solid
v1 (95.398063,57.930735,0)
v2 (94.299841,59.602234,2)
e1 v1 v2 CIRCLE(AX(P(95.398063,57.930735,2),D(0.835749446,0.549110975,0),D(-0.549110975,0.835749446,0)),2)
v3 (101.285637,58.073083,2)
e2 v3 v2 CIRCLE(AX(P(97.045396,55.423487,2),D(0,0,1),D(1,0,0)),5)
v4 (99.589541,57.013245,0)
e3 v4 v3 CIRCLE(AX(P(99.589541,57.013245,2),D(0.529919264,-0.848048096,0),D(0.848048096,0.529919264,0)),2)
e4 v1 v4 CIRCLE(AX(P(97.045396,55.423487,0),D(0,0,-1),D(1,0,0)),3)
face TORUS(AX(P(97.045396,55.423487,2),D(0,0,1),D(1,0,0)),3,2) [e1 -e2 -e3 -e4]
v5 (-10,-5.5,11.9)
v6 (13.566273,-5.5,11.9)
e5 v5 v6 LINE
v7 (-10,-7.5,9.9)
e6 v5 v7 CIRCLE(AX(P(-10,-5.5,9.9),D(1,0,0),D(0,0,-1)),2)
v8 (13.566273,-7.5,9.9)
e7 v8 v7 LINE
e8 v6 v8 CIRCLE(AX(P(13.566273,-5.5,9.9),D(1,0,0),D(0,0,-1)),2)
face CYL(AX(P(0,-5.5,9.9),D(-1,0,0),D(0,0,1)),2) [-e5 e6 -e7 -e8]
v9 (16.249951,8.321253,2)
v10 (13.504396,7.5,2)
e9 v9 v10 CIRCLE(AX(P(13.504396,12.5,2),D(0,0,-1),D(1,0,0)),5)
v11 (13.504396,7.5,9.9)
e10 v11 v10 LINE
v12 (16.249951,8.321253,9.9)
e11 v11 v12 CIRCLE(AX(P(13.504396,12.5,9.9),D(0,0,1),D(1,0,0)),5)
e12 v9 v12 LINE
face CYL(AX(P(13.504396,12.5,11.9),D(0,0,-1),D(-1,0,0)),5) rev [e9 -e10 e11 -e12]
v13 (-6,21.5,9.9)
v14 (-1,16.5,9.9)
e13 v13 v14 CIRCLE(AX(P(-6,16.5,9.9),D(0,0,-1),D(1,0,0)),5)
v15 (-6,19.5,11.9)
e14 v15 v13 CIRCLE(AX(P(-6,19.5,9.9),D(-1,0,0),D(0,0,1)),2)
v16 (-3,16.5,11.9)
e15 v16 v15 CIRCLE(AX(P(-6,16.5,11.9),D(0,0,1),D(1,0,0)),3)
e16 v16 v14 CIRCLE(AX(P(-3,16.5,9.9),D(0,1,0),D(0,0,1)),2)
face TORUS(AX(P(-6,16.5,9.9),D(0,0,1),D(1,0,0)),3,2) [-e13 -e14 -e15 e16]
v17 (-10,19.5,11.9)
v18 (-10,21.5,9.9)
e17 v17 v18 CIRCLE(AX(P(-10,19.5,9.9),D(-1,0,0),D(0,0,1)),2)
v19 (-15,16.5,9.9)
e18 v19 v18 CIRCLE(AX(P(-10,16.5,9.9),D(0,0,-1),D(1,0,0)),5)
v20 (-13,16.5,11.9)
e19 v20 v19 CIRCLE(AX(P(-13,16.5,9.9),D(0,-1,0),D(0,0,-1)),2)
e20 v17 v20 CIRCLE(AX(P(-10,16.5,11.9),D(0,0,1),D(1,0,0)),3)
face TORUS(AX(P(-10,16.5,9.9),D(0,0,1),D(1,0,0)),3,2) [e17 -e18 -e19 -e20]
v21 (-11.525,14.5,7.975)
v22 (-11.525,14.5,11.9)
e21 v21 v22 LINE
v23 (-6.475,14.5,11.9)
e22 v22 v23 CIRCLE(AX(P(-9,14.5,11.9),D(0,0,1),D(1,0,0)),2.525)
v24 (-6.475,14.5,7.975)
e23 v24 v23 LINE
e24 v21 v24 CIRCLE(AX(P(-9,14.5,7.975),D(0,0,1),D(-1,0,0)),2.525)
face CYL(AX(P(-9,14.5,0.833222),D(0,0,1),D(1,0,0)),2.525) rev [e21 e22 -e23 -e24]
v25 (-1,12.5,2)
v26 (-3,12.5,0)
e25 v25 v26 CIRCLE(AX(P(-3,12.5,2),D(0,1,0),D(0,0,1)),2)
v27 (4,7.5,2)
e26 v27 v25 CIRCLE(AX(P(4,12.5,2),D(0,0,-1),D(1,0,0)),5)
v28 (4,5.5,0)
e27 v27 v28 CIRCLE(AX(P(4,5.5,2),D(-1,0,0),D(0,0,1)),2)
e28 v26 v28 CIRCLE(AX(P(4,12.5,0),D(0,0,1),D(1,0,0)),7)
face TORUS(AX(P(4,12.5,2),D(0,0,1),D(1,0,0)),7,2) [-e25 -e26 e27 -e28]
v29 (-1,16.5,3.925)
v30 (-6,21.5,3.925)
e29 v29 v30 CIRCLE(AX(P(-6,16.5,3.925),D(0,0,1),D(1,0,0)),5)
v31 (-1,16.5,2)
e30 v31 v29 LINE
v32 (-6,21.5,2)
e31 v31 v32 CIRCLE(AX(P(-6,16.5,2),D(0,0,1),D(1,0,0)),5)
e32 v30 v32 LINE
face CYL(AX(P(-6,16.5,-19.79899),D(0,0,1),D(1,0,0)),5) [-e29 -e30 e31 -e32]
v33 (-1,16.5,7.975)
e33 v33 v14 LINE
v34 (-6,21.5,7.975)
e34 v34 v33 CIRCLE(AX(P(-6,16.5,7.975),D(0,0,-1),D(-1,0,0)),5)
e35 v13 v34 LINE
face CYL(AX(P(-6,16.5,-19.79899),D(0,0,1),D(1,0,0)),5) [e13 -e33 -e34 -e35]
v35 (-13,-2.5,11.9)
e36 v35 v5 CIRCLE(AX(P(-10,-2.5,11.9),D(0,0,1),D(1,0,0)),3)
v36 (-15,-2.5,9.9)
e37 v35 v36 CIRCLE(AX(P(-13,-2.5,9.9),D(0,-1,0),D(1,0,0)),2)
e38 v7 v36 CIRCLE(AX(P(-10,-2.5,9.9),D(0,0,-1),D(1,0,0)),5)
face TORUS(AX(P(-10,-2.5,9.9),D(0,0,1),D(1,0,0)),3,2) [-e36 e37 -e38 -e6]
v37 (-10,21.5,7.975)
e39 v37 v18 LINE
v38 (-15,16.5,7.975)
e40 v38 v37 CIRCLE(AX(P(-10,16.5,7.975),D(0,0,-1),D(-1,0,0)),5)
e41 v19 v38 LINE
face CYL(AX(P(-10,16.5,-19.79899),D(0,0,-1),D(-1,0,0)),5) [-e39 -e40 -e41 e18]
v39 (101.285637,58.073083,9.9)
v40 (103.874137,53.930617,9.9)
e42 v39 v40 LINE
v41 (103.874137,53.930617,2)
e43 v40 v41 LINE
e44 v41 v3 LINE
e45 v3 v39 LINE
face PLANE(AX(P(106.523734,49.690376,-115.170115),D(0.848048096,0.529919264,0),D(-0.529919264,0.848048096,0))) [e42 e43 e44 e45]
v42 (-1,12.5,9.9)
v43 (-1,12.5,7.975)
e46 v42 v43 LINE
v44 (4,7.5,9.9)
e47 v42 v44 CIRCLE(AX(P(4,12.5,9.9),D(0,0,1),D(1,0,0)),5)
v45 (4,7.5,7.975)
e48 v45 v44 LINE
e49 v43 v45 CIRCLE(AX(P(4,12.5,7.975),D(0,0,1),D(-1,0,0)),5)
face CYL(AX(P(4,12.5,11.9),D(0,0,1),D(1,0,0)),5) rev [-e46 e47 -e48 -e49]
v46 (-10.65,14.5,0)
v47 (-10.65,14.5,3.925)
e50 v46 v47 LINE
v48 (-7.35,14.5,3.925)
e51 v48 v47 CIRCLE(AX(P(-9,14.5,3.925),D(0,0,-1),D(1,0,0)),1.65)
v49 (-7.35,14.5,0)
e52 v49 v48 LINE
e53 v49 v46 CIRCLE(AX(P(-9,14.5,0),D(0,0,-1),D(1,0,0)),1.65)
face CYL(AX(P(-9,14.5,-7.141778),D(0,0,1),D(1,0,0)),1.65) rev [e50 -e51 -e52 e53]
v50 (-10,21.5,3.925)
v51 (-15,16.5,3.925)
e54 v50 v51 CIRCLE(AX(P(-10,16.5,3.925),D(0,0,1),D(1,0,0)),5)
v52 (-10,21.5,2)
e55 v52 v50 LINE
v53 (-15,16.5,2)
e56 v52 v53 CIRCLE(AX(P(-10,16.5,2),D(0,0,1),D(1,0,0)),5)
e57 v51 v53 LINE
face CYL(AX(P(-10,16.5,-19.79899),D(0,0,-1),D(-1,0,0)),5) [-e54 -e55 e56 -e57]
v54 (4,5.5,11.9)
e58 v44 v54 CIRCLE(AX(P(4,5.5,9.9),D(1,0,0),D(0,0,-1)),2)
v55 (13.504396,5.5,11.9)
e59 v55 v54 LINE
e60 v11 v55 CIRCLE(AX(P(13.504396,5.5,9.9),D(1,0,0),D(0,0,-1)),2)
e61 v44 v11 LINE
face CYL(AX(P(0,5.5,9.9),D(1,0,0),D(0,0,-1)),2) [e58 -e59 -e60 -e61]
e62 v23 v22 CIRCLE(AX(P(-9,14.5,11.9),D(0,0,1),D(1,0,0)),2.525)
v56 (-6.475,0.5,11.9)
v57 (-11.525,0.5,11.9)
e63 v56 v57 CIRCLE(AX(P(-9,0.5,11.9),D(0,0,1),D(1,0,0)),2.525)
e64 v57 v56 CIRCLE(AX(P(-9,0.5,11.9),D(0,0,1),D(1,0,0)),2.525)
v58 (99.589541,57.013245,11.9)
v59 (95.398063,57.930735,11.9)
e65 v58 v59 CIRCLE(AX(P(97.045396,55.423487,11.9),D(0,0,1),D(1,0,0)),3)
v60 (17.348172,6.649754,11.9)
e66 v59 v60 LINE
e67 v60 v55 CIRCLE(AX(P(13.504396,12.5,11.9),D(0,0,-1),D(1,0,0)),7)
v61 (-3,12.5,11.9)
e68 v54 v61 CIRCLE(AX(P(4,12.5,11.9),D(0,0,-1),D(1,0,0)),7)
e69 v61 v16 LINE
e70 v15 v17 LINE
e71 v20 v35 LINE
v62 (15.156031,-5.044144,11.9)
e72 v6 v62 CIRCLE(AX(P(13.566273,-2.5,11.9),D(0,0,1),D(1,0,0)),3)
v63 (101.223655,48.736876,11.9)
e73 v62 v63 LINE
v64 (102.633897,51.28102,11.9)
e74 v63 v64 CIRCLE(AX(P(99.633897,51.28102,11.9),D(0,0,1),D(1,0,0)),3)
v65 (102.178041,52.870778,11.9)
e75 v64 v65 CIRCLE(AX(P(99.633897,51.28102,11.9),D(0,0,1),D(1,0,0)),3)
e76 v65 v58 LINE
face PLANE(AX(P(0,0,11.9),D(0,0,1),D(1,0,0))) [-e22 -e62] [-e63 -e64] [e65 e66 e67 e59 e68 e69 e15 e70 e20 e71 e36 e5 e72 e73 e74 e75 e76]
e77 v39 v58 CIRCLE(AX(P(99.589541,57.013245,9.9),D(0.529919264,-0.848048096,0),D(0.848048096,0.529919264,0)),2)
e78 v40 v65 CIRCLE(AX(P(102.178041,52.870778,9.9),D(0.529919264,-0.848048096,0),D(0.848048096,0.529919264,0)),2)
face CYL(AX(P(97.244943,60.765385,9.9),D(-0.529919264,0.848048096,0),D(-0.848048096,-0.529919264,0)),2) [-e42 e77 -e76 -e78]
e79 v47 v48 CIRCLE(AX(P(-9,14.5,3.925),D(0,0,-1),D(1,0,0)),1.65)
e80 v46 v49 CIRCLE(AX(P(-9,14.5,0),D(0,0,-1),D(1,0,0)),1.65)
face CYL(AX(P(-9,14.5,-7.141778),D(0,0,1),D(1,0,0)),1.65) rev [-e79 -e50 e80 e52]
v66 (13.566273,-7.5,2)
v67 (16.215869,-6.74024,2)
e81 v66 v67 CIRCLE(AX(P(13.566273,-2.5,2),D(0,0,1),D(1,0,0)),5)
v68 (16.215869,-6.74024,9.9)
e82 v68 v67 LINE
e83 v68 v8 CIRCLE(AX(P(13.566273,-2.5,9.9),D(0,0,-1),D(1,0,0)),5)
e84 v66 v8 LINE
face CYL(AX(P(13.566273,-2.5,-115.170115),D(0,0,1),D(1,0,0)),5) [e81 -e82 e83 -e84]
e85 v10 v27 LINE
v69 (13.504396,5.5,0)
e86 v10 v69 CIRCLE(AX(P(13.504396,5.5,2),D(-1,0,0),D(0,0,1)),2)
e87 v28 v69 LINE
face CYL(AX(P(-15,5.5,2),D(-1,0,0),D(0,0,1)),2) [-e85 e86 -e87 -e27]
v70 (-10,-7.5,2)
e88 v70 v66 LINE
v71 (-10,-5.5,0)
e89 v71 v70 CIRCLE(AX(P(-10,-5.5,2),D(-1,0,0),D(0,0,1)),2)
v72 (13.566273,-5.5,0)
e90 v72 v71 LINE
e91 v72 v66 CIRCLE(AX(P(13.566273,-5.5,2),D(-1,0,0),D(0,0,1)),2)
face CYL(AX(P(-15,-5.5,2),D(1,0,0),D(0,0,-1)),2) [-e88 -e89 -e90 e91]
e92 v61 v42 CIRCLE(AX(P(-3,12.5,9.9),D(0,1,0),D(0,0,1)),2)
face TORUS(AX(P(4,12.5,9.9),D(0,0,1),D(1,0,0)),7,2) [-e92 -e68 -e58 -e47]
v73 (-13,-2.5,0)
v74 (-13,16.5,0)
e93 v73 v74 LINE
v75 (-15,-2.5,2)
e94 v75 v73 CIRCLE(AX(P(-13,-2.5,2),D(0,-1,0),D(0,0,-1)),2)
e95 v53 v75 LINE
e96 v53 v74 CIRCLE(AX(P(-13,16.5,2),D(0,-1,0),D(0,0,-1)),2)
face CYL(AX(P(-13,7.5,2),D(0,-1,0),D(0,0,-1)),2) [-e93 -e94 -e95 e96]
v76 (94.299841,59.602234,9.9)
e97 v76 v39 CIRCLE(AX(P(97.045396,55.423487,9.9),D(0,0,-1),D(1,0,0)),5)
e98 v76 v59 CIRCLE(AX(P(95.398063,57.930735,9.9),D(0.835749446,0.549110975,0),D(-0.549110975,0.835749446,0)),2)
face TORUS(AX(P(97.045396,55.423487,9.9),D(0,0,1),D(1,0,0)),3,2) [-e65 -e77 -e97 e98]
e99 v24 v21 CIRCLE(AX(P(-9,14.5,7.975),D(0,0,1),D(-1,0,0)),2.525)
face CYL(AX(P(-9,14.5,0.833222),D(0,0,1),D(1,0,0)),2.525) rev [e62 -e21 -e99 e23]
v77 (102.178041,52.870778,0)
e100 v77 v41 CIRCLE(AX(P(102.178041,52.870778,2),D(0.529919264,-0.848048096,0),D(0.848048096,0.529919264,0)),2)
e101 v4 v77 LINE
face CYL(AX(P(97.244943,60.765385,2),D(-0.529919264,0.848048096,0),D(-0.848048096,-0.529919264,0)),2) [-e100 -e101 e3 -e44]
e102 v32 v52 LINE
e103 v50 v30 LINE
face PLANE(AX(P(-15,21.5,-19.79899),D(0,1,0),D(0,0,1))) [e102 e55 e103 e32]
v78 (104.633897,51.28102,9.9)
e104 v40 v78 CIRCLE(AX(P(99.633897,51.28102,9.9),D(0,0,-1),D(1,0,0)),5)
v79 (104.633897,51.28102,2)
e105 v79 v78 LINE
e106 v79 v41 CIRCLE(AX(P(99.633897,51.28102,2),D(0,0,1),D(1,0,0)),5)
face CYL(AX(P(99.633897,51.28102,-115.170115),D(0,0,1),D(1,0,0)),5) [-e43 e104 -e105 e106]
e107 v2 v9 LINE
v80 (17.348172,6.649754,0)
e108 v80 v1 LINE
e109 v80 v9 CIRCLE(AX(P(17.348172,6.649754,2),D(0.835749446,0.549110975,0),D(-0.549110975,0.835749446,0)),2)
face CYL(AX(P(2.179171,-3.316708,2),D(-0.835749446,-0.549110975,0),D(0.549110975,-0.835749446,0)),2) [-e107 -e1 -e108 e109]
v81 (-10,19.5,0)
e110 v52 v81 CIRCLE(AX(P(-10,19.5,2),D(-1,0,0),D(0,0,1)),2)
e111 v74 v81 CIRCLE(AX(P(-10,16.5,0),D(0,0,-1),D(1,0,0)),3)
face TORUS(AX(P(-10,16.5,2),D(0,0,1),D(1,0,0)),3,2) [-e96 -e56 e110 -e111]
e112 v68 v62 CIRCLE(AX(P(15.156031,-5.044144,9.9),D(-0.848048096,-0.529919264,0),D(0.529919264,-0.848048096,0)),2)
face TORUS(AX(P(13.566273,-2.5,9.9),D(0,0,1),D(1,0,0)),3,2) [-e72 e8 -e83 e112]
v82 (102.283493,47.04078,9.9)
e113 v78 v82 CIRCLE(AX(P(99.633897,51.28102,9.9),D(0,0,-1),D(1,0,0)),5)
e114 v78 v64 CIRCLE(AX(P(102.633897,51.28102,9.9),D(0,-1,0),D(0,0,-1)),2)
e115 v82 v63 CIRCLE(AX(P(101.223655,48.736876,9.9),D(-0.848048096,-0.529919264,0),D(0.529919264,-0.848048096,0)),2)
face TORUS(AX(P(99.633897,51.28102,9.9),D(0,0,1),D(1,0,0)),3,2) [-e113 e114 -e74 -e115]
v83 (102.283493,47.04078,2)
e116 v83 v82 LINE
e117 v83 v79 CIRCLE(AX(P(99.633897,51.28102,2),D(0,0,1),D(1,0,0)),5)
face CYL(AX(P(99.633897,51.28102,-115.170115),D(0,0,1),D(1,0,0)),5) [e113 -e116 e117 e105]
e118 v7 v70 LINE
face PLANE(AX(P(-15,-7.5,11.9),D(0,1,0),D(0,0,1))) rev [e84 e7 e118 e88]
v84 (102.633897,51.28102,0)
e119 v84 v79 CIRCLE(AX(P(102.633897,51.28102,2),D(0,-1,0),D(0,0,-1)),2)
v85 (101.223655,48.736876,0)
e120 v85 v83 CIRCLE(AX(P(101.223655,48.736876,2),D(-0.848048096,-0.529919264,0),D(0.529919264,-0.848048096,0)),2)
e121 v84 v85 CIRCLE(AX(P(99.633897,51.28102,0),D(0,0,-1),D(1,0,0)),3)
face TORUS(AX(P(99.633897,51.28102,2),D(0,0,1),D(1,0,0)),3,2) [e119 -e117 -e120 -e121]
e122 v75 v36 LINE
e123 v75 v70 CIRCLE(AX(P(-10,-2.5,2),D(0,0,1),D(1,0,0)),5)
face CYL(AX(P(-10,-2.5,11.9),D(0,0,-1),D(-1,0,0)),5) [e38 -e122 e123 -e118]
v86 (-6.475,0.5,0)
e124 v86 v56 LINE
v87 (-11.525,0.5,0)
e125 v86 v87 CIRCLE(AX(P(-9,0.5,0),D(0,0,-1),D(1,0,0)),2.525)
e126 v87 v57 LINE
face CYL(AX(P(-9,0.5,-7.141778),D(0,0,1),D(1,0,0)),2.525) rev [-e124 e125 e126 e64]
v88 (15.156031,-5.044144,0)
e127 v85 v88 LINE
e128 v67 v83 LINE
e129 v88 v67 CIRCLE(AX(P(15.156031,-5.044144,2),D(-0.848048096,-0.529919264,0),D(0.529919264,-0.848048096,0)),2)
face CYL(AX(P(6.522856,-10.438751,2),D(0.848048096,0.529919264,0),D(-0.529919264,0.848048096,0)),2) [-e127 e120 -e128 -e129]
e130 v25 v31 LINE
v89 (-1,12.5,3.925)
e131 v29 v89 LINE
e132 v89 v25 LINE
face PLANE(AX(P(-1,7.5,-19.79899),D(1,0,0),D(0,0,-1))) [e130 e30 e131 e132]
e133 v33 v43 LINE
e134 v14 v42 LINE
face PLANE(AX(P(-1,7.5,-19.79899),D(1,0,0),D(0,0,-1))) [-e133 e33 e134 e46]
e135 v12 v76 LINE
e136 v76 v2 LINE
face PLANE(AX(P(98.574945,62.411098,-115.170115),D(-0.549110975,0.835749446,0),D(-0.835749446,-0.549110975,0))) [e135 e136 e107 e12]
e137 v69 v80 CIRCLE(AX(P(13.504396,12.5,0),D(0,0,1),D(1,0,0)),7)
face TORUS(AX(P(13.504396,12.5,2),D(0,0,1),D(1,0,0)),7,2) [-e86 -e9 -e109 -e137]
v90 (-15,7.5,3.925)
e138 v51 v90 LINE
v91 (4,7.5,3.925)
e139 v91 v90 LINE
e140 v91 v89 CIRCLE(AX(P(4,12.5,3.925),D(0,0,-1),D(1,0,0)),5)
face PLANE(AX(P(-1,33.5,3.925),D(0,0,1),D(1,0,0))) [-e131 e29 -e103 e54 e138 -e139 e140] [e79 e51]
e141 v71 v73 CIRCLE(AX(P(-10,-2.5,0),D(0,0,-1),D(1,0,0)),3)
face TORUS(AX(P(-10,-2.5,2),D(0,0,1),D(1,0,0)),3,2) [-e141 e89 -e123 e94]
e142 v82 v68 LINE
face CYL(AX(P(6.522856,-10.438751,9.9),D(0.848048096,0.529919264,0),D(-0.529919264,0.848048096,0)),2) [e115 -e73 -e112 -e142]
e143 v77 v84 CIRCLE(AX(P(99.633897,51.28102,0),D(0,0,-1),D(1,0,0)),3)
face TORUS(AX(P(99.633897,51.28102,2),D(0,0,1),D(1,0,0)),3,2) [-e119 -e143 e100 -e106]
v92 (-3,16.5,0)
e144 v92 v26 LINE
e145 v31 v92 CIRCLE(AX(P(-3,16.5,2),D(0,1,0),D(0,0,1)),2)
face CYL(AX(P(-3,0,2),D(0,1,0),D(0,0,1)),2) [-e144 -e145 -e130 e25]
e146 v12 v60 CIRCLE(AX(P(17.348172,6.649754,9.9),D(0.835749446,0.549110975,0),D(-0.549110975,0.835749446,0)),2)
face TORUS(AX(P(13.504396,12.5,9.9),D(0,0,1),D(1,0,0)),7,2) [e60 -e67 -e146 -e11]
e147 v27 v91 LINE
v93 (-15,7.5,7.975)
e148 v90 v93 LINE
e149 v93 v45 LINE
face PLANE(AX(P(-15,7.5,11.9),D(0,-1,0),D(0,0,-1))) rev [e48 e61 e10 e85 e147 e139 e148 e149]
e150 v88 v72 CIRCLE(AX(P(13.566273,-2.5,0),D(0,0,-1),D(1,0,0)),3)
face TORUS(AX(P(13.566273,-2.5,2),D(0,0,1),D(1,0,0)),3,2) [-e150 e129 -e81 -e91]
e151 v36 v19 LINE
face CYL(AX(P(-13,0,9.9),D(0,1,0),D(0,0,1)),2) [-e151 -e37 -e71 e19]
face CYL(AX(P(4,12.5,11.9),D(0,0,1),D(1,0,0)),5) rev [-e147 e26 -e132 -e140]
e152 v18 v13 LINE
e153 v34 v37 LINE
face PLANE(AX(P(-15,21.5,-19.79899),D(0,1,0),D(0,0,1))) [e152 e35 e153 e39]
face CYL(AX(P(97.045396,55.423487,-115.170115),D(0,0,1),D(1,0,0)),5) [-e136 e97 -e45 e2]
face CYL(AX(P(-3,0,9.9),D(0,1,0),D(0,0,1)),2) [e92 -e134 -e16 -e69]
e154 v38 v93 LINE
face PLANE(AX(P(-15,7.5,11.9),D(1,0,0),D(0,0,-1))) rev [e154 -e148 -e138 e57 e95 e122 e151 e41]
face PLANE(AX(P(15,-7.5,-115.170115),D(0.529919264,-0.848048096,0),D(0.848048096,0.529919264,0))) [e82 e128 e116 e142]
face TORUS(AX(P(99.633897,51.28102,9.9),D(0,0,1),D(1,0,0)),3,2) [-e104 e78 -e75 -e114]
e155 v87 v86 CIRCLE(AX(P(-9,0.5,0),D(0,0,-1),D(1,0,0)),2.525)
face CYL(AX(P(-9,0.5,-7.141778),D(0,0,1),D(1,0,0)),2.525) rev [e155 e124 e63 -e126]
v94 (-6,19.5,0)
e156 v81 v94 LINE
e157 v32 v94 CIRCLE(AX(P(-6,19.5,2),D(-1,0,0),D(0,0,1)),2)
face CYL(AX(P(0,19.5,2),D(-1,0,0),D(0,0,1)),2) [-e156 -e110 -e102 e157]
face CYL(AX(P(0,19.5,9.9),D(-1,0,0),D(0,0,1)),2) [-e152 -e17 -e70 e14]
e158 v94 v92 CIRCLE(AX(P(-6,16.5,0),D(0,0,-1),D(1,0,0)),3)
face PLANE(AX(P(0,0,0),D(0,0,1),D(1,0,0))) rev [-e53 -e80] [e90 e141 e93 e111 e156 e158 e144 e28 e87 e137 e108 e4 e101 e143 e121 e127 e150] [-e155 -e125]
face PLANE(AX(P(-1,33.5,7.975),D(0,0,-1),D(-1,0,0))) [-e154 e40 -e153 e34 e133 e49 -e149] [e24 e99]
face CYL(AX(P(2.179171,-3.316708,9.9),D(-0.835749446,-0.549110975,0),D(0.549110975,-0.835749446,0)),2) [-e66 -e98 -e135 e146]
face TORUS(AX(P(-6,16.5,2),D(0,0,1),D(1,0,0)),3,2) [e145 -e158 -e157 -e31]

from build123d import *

# Parameters (mm, degrees)
SKETCH1_W           = 30
SKETCH1_H           = 15
BOSS_EXTRUDE1_DEPTH = 11.9
SKETCH2_W           = 14
SKETCH2_H           = 14
BOSS_EXTRUDE2_DEPTH = 11.9
SKETCH3_R           = 2.525
SKETCH3_R_2         = 1.65
CUT_EXTRUDE2_DEPTH  = 11.9
BOSS_EXTRUDE3_DEPTH = 11.9
SKETCH5_W           = 14
SKETCH5_H           = 4.05
CUT_EXTRUDE3_DEPTH  = 26
FILLET1_R           = 5
FILLET2_R           = 2
SKETCH6_R           = 2.525
CUT_EXTRUDE4_DEPTH  = 3.925


with BuildPart() as part:
    # Sketch1 → Boss-Extrude1 (new body)
    with BuildSketch(Plane.XY):
        Rectangle(SKETCH1_W, SKETCH1_H)
    extrude(amount=BOSS_EXTRUDE1_DEPTH)

    # Sketch2 → Boss-Extrude2 (add)
    with BuildSketch(Plane.XY.offset(11.9)):
        with Locations((-8, 14.5)):
            Rectangle(SKETCH2_W, SKETCH2_H)
    extrude(amount=-BOSS_EXTRUDE2_DEPTH)

    # Sketch3 → Cut-Extrude2 (cut)
    with BuildSketch(Plane.XY.offset(11.9)):
        with Locations((-9, 0.5)):
            Circle(SKETCH3_R)
        with Locations((-9, 14.5)):
            Circle(SKETCH3_R_2)
    extrude(amount=-CUT_EXTRUDE2_DEPTH, mode=Mode.SUBTRACT)

    # Sketch4 → Boss-Extrude3 (add)
    with BuildSketch(Plane.XY.offset(11.9)):
        Polygon((15, -7.5), (106.523733582, 49.690376088), (98.574944619, 62.41109753), (15, 7.5), align=None)
    extrude(amount=-BOSS_EXTRUDE3_DEPTH)

    # Sketch5 → Cut-Extrude3 (cut)
    with BuildSketch(Plane(origin=(0, 7.5, 0), x_dir=(1, 0, 0), z_dir=(0, 1, 0))):
        with Locations((-8, -5.95)):
            Rectangle(SKETCH5_W, SKETCH5_H)
    extrude(amount=CUT_EXTRUDE3_DEPTH, mode=Mode.SUBTRACT)

    # Fillet1
    fillet1_edges = [part.edges().sort_by_distance(p)[0] for p in [
        (-15, 21.5, 1.9625),
        (-1, 21.5, 1.9625),
        (-1, 7.5, 1.9625),
        (98.574944619, 62.41109753, 5.95),
        (106.523733582, 49.690376088, 5.95),
        (-1, 21.5, 9.9375),
        (-1, 7.5, 9.9375),
        (-15, 21.5, 9.9375),
        (15, -7.5, 5.95),
        (-15, -7.5, 5.95),
        (15, 7.5, 5.95),
    ]]
    fillet(fillet1_edges, radius=FILLET1_R)

    # Fillet2
    fillet2_edges = [part.edges().sort_by_distance(p)[0] for p in [
        (14.937271043, 7.709711065, 0),
        (14.937271043, 7.709711065, 11.9),
        (0.464466094, 8.964466094, 11.9),
        (0.464466094, 8.964466094, 0),
        (102.579887045, 56.001849878, 0),
        (102.579887045, 56.001849878, 11.9),
        (1.783136536, -7.5, 11.9),
        (59.249681247, 20.150269643, 11.9),
        (55.274895994, 33.961743433, 11.9),
        (8.75219782, 7.5, 11.9),
        (-1, 14.5, 11.9),
        (-8, 21.5, 11.9),
        (-15, 7, 11.9),
        (-13.535533906, 20.035533906, 11.9),
        (-2.464466094, 20.035533906, 11.9),
        (-13.535533906, -6.035533906, 11.9),
        (14.94445985, -7.30630848, 11.9),
        (104.505747104, 50.156264976, 11.9),
        (98.114553442, 60.307839752, 11.9),
        (55.274895994, 33.961743433, 0),
        (8.75219782, 7.5, 0),
        (59.249681247, 20.150269643, 0),
        (1.783136536, -7.5, 0),
        (-15, 7, 0),
        (-8, 21.5, 0),
        (-1, 14.5, 0),
        (-13.535533906, 20.035533906, 0),
        (-2.464466094, 20.035533906, 0),
        (-13.535533906, -6.035533906, 0),
        (14.94445985, -7.30630848, 0),
        (104.505747104, 50.156264976, 0),
        (98.114553442, 60.307839752, 0),
    ]]
    fillet(fillet2_edges, radius=FILLET2_R)

    # Sketch6 → Cut-Extrude4 (cut)
    with BuildSketch(Plane.XY.offset(11.9)):
        with Locations((-9, 14.5)):
            Circle(SKETCH6_R)
    extrude(amount=-CUT_EXTRUDE4_DEPTH, mode=Mode.SUBTRACT)


solid = part.part
